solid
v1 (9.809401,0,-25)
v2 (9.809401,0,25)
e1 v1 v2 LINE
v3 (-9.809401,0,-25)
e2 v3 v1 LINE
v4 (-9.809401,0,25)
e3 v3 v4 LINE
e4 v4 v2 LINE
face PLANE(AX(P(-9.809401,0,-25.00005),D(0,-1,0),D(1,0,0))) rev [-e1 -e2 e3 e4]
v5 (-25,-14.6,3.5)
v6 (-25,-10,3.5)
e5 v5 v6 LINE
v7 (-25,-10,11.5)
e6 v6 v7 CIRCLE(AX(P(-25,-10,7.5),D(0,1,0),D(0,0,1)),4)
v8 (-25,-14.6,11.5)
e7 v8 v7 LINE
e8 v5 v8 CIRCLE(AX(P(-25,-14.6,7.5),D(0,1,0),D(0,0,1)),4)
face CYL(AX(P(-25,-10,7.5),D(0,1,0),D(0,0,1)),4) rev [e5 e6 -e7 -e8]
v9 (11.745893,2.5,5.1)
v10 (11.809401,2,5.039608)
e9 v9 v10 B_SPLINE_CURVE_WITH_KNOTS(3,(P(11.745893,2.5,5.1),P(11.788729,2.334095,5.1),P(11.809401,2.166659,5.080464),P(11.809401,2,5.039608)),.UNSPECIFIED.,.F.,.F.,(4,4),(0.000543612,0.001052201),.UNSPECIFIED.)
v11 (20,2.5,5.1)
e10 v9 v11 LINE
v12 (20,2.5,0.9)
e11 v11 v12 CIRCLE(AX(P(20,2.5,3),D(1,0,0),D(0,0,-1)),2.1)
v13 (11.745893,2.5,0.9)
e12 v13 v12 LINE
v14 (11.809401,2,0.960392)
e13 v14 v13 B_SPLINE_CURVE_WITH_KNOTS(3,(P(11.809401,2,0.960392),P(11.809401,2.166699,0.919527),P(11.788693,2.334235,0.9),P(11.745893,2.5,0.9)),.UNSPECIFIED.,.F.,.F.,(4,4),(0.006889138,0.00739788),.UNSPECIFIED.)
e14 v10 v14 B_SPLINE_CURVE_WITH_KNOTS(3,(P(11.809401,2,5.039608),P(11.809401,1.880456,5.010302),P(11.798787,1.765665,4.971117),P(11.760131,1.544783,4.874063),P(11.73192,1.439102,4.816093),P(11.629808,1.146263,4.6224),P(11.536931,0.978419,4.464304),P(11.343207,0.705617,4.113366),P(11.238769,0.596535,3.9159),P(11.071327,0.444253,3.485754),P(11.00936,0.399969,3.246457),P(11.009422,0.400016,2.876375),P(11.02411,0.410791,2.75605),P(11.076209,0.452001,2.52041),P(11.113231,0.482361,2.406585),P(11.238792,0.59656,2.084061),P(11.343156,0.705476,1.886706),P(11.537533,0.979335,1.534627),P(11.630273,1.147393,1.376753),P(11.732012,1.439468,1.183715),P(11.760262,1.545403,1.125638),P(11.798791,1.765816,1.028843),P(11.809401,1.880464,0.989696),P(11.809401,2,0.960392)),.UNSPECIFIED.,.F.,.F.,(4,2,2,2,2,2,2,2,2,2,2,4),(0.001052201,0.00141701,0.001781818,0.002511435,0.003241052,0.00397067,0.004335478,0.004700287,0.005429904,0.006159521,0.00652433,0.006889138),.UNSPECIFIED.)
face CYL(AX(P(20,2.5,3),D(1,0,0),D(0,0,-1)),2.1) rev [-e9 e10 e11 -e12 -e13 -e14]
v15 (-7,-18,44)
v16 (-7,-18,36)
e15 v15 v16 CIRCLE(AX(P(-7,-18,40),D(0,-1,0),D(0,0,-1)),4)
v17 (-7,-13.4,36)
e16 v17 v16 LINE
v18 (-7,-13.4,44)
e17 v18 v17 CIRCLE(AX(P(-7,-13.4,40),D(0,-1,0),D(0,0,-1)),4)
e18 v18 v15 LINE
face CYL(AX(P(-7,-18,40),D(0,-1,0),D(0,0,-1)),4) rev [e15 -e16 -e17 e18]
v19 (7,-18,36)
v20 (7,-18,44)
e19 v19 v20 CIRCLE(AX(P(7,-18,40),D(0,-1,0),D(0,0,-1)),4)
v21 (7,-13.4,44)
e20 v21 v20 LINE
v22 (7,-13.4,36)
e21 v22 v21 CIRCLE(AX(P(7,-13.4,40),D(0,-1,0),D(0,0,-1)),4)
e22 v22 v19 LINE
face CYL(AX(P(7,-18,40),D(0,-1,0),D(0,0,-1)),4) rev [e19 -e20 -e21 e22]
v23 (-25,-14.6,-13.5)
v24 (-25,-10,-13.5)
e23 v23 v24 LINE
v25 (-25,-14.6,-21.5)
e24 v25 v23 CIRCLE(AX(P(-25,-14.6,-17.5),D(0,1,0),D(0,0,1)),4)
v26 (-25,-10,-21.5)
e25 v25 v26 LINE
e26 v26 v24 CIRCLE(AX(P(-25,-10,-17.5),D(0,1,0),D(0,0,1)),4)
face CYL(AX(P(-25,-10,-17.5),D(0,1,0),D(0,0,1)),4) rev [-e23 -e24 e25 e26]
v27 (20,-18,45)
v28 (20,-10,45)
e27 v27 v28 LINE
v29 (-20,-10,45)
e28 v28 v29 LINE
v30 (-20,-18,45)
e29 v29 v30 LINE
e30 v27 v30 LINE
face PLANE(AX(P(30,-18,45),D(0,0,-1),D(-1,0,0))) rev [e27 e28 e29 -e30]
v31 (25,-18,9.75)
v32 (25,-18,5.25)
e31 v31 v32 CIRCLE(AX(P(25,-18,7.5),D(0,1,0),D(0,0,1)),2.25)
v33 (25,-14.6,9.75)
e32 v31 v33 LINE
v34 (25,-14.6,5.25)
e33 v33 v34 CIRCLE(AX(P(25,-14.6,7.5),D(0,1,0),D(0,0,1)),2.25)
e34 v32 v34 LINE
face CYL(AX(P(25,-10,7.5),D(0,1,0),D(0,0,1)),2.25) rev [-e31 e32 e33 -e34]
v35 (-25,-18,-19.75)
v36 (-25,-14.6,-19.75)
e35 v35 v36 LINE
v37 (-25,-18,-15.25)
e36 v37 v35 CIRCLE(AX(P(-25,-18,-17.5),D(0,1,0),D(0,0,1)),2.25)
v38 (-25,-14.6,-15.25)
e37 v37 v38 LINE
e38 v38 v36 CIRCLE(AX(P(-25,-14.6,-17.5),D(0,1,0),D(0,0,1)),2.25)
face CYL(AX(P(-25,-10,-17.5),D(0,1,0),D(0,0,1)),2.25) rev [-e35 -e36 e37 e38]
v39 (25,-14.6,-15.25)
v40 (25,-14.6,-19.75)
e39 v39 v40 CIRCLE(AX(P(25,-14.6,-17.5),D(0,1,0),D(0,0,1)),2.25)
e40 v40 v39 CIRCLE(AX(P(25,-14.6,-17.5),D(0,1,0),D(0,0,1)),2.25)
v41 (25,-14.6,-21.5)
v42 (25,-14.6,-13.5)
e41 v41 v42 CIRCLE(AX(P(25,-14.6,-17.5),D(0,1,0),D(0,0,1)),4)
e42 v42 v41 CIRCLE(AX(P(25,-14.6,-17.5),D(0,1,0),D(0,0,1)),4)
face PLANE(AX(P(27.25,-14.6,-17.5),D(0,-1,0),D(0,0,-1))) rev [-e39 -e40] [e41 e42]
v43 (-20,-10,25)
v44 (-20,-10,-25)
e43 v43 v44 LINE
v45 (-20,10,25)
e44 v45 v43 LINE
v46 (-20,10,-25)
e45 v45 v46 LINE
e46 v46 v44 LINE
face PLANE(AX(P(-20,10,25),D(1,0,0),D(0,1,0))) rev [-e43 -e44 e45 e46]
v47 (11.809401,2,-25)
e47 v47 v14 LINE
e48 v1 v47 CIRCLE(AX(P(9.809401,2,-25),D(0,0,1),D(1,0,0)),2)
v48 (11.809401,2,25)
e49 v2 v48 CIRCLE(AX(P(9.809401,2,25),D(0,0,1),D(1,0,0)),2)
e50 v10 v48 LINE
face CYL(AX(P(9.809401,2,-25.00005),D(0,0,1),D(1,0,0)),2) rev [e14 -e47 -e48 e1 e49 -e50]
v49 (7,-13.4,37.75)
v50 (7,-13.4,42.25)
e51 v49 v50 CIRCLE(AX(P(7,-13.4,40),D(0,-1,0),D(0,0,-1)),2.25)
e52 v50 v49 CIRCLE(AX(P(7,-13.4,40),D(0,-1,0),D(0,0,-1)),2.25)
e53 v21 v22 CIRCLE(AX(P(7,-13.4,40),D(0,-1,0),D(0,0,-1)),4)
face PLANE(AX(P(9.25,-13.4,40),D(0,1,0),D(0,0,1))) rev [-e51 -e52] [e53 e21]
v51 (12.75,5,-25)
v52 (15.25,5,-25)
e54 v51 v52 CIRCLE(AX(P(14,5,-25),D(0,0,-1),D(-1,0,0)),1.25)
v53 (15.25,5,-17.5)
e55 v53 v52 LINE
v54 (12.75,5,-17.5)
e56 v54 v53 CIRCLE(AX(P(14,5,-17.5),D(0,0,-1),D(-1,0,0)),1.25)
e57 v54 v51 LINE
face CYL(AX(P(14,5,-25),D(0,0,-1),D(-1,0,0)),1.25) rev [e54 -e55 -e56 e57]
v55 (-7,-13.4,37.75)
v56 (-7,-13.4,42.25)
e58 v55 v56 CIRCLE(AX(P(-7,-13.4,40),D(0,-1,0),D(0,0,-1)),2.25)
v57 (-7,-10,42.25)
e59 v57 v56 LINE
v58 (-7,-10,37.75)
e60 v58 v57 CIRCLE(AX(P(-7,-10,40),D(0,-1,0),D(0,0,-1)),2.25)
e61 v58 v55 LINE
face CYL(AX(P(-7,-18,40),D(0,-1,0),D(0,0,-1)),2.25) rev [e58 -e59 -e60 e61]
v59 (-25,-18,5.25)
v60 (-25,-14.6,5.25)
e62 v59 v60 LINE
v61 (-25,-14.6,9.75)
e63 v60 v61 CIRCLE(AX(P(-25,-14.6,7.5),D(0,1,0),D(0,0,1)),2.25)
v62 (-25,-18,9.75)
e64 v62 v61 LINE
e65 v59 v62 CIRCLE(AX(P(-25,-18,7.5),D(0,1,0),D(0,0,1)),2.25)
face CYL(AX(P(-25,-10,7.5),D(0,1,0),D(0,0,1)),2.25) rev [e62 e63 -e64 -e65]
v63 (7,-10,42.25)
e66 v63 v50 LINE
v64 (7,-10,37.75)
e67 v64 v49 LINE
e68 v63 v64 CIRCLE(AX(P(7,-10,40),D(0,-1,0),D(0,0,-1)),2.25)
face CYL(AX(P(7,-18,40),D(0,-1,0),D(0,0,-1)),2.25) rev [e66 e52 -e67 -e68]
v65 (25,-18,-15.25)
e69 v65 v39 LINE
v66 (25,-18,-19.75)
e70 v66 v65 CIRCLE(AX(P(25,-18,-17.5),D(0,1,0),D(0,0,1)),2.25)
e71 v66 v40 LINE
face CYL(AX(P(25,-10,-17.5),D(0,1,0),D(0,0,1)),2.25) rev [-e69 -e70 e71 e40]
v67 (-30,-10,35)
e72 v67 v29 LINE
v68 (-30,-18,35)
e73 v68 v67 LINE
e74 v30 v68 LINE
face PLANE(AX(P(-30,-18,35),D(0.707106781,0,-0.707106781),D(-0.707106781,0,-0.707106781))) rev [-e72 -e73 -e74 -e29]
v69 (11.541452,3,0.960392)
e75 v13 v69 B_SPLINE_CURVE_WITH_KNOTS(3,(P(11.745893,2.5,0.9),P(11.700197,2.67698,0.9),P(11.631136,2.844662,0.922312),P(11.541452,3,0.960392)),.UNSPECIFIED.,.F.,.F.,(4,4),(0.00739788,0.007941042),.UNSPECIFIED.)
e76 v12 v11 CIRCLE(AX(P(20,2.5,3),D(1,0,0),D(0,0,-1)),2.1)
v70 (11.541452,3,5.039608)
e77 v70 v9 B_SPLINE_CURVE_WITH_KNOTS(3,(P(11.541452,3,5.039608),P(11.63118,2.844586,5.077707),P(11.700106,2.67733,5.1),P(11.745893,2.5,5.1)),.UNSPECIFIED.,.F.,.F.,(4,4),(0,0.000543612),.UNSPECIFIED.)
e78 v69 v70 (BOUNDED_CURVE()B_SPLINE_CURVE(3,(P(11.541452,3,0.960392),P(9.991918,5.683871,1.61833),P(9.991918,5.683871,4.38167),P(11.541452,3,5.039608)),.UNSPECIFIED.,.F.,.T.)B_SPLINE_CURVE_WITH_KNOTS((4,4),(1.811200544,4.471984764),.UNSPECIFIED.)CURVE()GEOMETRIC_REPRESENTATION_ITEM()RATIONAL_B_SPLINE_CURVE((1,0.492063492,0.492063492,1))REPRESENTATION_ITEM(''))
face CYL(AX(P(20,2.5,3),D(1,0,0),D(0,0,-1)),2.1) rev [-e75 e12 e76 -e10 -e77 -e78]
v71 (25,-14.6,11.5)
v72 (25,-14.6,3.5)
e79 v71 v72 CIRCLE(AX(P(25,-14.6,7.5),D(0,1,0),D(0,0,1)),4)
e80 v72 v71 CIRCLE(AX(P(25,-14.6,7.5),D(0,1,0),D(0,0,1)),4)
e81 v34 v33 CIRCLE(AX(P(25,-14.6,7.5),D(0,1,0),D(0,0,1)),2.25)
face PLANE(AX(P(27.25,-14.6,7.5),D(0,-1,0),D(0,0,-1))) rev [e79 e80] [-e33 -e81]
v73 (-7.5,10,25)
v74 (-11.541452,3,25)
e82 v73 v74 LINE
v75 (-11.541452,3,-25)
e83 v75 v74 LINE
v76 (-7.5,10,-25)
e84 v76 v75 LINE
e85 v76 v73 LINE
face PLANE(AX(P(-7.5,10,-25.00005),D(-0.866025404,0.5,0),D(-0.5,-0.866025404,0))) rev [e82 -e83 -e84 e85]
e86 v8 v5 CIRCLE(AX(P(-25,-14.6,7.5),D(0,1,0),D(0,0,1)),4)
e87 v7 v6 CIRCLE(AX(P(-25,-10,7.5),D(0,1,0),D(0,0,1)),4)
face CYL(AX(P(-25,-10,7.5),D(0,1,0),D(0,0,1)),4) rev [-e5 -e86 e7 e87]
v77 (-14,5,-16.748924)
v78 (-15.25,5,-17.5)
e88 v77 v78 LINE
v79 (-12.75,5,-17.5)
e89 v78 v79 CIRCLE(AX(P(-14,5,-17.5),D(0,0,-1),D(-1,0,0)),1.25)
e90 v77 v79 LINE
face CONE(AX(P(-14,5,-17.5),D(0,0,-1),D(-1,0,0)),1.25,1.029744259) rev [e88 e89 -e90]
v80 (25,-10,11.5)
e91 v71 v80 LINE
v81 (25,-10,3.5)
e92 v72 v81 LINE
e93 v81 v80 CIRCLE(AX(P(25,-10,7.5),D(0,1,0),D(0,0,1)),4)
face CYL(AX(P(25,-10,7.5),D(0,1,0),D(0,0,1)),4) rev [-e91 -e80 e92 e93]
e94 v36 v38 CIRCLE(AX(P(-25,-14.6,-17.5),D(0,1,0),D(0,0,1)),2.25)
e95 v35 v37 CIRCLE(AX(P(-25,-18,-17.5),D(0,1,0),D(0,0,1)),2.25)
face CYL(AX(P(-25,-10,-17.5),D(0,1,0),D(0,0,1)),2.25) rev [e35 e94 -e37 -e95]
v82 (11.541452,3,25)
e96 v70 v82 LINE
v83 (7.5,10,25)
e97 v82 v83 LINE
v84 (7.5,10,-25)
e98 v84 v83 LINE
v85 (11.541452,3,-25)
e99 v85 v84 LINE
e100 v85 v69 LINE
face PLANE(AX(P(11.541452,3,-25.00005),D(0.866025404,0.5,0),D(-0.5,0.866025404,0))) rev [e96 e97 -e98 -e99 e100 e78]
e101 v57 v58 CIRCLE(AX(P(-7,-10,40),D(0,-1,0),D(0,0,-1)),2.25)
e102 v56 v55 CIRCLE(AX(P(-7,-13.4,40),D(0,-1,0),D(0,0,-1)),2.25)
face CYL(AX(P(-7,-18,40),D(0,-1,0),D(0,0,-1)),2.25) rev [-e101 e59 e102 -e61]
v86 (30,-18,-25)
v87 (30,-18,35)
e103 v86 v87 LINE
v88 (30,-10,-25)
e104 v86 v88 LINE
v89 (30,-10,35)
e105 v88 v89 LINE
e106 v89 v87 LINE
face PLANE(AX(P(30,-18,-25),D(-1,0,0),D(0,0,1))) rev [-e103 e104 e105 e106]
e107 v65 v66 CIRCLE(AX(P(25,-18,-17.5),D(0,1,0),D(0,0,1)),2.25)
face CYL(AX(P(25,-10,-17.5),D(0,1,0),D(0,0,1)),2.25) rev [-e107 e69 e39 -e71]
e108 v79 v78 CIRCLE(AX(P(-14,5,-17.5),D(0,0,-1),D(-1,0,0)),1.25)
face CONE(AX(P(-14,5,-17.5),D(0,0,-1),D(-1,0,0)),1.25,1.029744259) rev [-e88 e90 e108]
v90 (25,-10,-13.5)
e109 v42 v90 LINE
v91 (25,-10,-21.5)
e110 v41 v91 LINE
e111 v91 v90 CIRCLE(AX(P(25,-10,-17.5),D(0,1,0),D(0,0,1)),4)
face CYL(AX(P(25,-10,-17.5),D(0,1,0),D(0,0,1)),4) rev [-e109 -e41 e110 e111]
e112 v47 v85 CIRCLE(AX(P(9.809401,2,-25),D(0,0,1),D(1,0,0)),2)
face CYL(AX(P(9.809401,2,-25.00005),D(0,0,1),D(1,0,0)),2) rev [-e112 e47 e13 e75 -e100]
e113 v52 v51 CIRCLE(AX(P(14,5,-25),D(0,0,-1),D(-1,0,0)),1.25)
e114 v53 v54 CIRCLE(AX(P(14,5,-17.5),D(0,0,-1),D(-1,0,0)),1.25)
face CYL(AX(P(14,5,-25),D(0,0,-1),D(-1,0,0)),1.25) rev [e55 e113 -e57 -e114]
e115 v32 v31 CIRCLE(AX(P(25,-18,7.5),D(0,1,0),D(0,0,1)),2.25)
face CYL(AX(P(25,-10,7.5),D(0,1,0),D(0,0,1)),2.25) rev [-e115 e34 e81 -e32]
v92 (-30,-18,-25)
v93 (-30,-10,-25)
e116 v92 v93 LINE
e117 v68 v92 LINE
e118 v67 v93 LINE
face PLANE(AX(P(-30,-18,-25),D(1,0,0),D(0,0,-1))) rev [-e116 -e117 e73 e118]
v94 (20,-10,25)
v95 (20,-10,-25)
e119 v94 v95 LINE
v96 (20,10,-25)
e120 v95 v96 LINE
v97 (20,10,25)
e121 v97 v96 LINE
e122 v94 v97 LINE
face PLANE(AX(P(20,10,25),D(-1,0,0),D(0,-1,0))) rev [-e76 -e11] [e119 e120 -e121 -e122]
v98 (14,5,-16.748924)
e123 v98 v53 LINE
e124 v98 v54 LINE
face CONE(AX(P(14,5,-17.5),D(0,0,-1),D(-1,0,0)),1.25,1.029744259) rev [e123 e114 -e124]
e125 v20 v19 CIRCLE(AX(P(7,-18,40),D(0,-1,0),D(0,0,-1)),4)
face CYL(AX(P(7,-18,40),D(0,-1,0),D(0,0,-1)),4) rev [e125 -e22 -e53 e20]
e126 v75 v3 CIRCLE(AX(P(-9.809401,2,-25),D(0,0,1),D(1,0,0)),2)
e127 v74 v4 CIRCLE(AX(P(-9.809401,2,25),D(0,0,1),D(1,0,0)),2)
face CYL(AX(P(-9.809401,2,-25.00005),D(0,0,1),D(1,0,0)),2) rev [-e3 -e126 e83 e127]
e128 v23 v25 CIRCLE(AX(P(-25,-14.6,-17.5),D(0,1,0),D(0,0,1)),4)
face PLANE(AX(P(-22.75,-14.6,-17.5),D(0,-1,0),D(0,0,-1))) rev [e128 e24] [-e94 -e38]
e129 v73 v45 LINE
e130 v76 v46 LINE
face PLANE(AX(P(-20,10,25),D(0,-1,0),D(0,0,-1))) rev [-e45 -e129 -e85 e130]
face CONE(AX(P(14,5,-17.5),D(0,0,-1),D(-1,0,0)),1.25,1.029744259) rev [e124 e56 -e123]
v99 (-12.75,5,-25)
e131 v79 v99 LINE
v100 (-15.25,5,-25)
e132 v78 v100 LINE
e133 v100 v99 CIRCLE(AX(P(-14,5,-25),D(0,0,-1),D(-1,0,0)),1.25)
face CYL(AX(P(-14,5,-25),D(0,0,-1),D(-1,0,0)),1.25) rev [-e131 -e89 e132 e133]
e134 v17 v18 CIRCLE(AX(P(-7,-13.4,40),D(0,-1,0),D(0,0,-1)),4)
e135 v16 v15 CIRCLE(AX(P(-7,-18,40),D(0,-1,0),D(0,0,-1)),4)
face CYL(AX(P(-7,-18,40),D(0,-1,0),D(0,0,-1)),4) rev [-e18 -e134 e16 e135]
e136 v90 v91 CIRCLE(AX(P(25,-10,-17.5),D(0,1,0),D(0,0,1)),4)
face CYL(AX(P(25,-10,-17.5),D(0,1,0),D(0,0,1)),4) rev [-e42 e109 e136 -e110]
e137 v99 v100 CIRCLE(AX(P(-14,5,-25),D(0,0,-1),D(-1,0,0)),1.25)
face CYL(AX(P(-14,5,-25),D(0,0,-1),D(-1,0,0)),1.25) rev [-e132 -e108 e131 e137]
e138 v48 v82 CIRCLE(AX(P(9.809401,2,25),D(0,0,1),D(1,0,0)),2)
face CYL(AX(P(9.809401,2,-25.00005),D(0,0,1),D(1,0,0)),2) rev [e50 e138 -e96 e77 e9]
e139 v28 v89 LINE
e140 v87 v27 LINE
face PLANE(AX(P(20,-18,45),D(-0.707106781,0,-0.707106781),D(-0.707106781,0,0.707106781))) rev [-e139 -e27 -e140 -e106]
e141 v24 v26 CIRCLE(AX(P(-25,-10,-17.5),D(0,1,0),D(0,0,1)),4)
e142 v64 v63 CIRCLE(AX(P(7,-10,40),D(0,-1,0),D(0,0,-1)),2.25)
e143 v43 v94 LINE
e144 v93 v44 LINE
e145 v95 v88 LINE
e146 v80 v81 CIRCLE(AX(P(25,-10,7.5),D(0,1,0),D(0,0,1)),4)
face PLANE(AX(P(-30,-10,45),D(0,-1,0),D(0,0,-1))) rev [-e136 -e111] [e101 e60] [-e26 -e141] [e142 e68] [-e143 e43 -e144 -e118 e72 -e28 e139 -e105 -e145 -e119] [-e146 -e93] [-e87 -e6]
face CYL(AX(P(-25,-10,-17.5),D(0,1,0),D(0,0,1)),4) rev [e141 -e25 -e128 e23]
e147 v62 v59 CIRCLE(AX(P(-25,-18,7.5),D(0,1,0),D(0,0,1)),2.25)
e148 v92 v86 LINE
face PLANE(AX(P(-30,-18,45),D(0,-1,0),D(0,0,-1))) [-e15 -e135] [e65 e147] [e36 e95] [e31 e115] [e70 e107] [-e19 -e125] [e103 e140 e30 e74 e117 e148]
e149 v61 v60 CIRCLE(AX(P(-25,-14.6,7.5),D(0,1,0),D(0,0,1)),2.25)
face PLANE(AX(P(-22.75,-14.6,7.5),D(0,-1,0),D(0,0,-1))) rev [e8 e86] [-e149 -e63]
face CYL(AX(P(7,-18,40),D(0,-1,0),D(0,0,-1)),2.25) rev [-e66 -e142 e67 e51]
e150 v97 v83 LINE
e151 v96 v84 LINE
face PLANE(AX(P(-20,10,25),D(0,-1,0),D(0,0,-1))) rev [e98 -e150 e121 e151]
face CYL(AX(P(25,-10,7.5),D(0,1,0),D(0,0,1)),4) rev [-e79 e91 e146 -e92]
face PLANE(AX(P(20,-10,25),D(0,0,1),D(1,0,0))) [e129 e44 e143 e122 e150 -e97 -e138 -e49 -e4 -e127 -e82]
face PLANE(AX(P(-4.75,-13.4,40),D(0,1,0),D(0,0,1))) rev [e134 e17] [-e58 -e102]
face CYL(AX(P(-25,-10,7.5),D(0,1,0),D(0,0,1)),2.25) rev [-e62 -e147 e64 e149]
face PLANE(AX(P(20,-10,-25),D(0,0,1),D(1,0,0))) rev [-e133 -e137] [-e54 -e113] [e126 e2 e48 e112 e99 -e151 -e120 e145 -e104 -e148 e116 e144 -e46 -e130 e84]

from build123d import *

# Parameters (mm, degrees)
SKETCH1_W                                            = 40
SKETCH1_H                                            = 20
BOSS_EXTRUDE1_DEPTH                                  = 25
SKETCH2_W                                            = 60
SKETCH2_H                                            = 70
BOSS_EXTRUDE2_DEPTH                                  = 8
CUT_EXTRUDE1_DEPTH                                   = 62.02458521
CHAMFER1_SIZE                                        = 10
HOLE_SIZE_PER_SOCKET_HEAD_CAP_SCREW_TYPE_D           = 4.5
HOLE_SIZE_PER_SOCKET_HEAD_CAP_SCREW_TYPE_CBORE_D     = 8
HOLE_SIZE_PER_SOCKET_HEAD_CAP_SCREW_TYPE_CBORE_DEPTH = 4.6
HOLE_SIZE_PER_SOCKET_HEAD_CAP_SCREW_2_D              = 4.5
HOLE_SIZE_PER_SOCKET_HEAD_CAP_SCREW_2_CBORE_D        = 8
HOLE_SIZE_PER_SOCKET_HEAD_CAP_SCREW_2_CBORE_DEPTH    = 4.6
M5_TAPPED_HOLE1_D                                    = 4.2
M5_TAPPED_HOLE1_DEPTH                                = 12.4
M5_TAPPED_HOLE1_TIP                                  = 1.2618073
M3_TAPPED_HOLE1_D                                    = 2.5
M3_TAPPED_HOLE1_DEPTH                                = 7.5
M3_TAPPED_HOLE1_TIP                                  = 0.751075774


with BuildPart() as part:
    # Sketch1 → Boss-Extrude1 (new, symmetric)
    with BuildSketch(Plane.XY):
        Rectangle(SKETCH1_W, SKETCH1_H)
    extrude(amount=BOSS_EXTRUDE1_DEPTH, both=True)

    # Sketch2 → Boss-Extrude2 (add)
    with BuildSketch(Plane.XZ.offset(10)):
        with Locations((0, 10)):
            Rectangle(SKETCH2_W, SKETCH2_H)
    extrude(amount=BOSS_EXTRUDE2_DEPTH)

    # Sketch3 → Cut-Extrude1 (cut, through all)
    with BuildSketch(Plane.XY.offset(25)):
        with BuildLine():
            Line((-7.5, 10), (-11.541451884, 3))
            ThreePointArc((-11.541451884, 3), (-11.541451884, 1), (-9.809401077, 0))
            Line((-9.809401077, 0), (9.809401077, 0))
            ThreePointArc((9.809401077, 0), (11.541451884, 1), (11.541451884, 3))
            Line((11.541451884, 3), (7.5, 10))
            Line((7.5, 10), (-7.5, 10))
        make_face()
    extrude(amount=-CUT_EXTRUDE1_DEPTH, mode=Mode.SUBTRACT)

    # Chamfer1
    chamfer1_edges = [part.edges().sort_by_distance(p)[0] for p in [
        (-30, -14, 45),
        (30, -14, 45),
    ]]
    chamfer(chamfer1_edges, length=CHAMFER1_SIZE)

    # Hole Size per Socket Head Cap Screw Type (through all)
    with Locations(Plane.XZ.offset(18)):
        with Locations((7, 40), (-7, 40)):
            CounterBoreHole(HOLE_SIZE_PER_SOCKET_HEAD_CAP_SCREW_TYPE_D / 2, HOLE_SIZE_PER_SOCKET_HEAD_CAP_SCREW_TYPE_CBORE_D / 2, HOLE_SIZE_PER_SOCKET_HEAD_CAP_SCREW_TYPE_CBORE_DEPTH)

    # Hole Size per Socket Head Cap Screw  2 (through all)
    with Locations(Plane(origin=(0, -10, 0), x_dir=(-1, 0, 0), z_dir=(0, 1, 0))):
        with Locations((25, -17.5), (25, 7.5), (-25, -17.5), (-25, 7.5)):
            CounterBoreHole(HOLE_SIZE_PER_SOCKET_HEAD_CAP_SCREW_2_D / 2, HOLE_SIZE_PER_SOCKET_HEAD_CAP_SCREW_2_CBORE_D / 2, HOLE_SIZE_PER_SOCKET_HEAD_CAP_SCREW_2_CBORE_DEPTH)

    # M5 Tapped Hole1
    with Locations(Plane(origin=(20, 0, 0), x_dir=(0, 0, -1), z_dir=(1, 0, 0))):
        with Locations((-3, 2.5)):
            Hole(M5_TAPPED_HOLE1_D / 2, depth=M5_TAPPED_HOLE1_DEPTH)
            with Locations((0, 0, -(M5_TAPPED_HOLE1_DEPTH + M5_TAPPED_HOLE1_TIP / 2))):  # 118° drill point
                Cone(0, M5_TAPPED_HOLE1_D / 2, M5_TAPPED_HOLE1_TIP, mode=Mode.SUBTRACT)

    # M3 Tapped Hole1
    with Locations(Plane(origin=(0, 0, -25), x_dir=(-1, 0, 0), z_dir=(0, 0, -1))):
        with Locations((14, 5), (-14, 5)):
            Hole(M3_TAPPED_HOLE1_D / 2, depth=M3_TAPPED_HOLE1_DEPTH)
            with Locations((0, 0, -(M3_TAPPED_HOLE1_DEPTH + M3_TAPPED_HOLE1_TIP / 2))):  # 118° drill point
                Cone(0, M3_TAPPED_HOLE1_D / 2, M3_TAPPED_HOLE1_TIP, mode=Mode.SUBTRACT)


solid = part.part
